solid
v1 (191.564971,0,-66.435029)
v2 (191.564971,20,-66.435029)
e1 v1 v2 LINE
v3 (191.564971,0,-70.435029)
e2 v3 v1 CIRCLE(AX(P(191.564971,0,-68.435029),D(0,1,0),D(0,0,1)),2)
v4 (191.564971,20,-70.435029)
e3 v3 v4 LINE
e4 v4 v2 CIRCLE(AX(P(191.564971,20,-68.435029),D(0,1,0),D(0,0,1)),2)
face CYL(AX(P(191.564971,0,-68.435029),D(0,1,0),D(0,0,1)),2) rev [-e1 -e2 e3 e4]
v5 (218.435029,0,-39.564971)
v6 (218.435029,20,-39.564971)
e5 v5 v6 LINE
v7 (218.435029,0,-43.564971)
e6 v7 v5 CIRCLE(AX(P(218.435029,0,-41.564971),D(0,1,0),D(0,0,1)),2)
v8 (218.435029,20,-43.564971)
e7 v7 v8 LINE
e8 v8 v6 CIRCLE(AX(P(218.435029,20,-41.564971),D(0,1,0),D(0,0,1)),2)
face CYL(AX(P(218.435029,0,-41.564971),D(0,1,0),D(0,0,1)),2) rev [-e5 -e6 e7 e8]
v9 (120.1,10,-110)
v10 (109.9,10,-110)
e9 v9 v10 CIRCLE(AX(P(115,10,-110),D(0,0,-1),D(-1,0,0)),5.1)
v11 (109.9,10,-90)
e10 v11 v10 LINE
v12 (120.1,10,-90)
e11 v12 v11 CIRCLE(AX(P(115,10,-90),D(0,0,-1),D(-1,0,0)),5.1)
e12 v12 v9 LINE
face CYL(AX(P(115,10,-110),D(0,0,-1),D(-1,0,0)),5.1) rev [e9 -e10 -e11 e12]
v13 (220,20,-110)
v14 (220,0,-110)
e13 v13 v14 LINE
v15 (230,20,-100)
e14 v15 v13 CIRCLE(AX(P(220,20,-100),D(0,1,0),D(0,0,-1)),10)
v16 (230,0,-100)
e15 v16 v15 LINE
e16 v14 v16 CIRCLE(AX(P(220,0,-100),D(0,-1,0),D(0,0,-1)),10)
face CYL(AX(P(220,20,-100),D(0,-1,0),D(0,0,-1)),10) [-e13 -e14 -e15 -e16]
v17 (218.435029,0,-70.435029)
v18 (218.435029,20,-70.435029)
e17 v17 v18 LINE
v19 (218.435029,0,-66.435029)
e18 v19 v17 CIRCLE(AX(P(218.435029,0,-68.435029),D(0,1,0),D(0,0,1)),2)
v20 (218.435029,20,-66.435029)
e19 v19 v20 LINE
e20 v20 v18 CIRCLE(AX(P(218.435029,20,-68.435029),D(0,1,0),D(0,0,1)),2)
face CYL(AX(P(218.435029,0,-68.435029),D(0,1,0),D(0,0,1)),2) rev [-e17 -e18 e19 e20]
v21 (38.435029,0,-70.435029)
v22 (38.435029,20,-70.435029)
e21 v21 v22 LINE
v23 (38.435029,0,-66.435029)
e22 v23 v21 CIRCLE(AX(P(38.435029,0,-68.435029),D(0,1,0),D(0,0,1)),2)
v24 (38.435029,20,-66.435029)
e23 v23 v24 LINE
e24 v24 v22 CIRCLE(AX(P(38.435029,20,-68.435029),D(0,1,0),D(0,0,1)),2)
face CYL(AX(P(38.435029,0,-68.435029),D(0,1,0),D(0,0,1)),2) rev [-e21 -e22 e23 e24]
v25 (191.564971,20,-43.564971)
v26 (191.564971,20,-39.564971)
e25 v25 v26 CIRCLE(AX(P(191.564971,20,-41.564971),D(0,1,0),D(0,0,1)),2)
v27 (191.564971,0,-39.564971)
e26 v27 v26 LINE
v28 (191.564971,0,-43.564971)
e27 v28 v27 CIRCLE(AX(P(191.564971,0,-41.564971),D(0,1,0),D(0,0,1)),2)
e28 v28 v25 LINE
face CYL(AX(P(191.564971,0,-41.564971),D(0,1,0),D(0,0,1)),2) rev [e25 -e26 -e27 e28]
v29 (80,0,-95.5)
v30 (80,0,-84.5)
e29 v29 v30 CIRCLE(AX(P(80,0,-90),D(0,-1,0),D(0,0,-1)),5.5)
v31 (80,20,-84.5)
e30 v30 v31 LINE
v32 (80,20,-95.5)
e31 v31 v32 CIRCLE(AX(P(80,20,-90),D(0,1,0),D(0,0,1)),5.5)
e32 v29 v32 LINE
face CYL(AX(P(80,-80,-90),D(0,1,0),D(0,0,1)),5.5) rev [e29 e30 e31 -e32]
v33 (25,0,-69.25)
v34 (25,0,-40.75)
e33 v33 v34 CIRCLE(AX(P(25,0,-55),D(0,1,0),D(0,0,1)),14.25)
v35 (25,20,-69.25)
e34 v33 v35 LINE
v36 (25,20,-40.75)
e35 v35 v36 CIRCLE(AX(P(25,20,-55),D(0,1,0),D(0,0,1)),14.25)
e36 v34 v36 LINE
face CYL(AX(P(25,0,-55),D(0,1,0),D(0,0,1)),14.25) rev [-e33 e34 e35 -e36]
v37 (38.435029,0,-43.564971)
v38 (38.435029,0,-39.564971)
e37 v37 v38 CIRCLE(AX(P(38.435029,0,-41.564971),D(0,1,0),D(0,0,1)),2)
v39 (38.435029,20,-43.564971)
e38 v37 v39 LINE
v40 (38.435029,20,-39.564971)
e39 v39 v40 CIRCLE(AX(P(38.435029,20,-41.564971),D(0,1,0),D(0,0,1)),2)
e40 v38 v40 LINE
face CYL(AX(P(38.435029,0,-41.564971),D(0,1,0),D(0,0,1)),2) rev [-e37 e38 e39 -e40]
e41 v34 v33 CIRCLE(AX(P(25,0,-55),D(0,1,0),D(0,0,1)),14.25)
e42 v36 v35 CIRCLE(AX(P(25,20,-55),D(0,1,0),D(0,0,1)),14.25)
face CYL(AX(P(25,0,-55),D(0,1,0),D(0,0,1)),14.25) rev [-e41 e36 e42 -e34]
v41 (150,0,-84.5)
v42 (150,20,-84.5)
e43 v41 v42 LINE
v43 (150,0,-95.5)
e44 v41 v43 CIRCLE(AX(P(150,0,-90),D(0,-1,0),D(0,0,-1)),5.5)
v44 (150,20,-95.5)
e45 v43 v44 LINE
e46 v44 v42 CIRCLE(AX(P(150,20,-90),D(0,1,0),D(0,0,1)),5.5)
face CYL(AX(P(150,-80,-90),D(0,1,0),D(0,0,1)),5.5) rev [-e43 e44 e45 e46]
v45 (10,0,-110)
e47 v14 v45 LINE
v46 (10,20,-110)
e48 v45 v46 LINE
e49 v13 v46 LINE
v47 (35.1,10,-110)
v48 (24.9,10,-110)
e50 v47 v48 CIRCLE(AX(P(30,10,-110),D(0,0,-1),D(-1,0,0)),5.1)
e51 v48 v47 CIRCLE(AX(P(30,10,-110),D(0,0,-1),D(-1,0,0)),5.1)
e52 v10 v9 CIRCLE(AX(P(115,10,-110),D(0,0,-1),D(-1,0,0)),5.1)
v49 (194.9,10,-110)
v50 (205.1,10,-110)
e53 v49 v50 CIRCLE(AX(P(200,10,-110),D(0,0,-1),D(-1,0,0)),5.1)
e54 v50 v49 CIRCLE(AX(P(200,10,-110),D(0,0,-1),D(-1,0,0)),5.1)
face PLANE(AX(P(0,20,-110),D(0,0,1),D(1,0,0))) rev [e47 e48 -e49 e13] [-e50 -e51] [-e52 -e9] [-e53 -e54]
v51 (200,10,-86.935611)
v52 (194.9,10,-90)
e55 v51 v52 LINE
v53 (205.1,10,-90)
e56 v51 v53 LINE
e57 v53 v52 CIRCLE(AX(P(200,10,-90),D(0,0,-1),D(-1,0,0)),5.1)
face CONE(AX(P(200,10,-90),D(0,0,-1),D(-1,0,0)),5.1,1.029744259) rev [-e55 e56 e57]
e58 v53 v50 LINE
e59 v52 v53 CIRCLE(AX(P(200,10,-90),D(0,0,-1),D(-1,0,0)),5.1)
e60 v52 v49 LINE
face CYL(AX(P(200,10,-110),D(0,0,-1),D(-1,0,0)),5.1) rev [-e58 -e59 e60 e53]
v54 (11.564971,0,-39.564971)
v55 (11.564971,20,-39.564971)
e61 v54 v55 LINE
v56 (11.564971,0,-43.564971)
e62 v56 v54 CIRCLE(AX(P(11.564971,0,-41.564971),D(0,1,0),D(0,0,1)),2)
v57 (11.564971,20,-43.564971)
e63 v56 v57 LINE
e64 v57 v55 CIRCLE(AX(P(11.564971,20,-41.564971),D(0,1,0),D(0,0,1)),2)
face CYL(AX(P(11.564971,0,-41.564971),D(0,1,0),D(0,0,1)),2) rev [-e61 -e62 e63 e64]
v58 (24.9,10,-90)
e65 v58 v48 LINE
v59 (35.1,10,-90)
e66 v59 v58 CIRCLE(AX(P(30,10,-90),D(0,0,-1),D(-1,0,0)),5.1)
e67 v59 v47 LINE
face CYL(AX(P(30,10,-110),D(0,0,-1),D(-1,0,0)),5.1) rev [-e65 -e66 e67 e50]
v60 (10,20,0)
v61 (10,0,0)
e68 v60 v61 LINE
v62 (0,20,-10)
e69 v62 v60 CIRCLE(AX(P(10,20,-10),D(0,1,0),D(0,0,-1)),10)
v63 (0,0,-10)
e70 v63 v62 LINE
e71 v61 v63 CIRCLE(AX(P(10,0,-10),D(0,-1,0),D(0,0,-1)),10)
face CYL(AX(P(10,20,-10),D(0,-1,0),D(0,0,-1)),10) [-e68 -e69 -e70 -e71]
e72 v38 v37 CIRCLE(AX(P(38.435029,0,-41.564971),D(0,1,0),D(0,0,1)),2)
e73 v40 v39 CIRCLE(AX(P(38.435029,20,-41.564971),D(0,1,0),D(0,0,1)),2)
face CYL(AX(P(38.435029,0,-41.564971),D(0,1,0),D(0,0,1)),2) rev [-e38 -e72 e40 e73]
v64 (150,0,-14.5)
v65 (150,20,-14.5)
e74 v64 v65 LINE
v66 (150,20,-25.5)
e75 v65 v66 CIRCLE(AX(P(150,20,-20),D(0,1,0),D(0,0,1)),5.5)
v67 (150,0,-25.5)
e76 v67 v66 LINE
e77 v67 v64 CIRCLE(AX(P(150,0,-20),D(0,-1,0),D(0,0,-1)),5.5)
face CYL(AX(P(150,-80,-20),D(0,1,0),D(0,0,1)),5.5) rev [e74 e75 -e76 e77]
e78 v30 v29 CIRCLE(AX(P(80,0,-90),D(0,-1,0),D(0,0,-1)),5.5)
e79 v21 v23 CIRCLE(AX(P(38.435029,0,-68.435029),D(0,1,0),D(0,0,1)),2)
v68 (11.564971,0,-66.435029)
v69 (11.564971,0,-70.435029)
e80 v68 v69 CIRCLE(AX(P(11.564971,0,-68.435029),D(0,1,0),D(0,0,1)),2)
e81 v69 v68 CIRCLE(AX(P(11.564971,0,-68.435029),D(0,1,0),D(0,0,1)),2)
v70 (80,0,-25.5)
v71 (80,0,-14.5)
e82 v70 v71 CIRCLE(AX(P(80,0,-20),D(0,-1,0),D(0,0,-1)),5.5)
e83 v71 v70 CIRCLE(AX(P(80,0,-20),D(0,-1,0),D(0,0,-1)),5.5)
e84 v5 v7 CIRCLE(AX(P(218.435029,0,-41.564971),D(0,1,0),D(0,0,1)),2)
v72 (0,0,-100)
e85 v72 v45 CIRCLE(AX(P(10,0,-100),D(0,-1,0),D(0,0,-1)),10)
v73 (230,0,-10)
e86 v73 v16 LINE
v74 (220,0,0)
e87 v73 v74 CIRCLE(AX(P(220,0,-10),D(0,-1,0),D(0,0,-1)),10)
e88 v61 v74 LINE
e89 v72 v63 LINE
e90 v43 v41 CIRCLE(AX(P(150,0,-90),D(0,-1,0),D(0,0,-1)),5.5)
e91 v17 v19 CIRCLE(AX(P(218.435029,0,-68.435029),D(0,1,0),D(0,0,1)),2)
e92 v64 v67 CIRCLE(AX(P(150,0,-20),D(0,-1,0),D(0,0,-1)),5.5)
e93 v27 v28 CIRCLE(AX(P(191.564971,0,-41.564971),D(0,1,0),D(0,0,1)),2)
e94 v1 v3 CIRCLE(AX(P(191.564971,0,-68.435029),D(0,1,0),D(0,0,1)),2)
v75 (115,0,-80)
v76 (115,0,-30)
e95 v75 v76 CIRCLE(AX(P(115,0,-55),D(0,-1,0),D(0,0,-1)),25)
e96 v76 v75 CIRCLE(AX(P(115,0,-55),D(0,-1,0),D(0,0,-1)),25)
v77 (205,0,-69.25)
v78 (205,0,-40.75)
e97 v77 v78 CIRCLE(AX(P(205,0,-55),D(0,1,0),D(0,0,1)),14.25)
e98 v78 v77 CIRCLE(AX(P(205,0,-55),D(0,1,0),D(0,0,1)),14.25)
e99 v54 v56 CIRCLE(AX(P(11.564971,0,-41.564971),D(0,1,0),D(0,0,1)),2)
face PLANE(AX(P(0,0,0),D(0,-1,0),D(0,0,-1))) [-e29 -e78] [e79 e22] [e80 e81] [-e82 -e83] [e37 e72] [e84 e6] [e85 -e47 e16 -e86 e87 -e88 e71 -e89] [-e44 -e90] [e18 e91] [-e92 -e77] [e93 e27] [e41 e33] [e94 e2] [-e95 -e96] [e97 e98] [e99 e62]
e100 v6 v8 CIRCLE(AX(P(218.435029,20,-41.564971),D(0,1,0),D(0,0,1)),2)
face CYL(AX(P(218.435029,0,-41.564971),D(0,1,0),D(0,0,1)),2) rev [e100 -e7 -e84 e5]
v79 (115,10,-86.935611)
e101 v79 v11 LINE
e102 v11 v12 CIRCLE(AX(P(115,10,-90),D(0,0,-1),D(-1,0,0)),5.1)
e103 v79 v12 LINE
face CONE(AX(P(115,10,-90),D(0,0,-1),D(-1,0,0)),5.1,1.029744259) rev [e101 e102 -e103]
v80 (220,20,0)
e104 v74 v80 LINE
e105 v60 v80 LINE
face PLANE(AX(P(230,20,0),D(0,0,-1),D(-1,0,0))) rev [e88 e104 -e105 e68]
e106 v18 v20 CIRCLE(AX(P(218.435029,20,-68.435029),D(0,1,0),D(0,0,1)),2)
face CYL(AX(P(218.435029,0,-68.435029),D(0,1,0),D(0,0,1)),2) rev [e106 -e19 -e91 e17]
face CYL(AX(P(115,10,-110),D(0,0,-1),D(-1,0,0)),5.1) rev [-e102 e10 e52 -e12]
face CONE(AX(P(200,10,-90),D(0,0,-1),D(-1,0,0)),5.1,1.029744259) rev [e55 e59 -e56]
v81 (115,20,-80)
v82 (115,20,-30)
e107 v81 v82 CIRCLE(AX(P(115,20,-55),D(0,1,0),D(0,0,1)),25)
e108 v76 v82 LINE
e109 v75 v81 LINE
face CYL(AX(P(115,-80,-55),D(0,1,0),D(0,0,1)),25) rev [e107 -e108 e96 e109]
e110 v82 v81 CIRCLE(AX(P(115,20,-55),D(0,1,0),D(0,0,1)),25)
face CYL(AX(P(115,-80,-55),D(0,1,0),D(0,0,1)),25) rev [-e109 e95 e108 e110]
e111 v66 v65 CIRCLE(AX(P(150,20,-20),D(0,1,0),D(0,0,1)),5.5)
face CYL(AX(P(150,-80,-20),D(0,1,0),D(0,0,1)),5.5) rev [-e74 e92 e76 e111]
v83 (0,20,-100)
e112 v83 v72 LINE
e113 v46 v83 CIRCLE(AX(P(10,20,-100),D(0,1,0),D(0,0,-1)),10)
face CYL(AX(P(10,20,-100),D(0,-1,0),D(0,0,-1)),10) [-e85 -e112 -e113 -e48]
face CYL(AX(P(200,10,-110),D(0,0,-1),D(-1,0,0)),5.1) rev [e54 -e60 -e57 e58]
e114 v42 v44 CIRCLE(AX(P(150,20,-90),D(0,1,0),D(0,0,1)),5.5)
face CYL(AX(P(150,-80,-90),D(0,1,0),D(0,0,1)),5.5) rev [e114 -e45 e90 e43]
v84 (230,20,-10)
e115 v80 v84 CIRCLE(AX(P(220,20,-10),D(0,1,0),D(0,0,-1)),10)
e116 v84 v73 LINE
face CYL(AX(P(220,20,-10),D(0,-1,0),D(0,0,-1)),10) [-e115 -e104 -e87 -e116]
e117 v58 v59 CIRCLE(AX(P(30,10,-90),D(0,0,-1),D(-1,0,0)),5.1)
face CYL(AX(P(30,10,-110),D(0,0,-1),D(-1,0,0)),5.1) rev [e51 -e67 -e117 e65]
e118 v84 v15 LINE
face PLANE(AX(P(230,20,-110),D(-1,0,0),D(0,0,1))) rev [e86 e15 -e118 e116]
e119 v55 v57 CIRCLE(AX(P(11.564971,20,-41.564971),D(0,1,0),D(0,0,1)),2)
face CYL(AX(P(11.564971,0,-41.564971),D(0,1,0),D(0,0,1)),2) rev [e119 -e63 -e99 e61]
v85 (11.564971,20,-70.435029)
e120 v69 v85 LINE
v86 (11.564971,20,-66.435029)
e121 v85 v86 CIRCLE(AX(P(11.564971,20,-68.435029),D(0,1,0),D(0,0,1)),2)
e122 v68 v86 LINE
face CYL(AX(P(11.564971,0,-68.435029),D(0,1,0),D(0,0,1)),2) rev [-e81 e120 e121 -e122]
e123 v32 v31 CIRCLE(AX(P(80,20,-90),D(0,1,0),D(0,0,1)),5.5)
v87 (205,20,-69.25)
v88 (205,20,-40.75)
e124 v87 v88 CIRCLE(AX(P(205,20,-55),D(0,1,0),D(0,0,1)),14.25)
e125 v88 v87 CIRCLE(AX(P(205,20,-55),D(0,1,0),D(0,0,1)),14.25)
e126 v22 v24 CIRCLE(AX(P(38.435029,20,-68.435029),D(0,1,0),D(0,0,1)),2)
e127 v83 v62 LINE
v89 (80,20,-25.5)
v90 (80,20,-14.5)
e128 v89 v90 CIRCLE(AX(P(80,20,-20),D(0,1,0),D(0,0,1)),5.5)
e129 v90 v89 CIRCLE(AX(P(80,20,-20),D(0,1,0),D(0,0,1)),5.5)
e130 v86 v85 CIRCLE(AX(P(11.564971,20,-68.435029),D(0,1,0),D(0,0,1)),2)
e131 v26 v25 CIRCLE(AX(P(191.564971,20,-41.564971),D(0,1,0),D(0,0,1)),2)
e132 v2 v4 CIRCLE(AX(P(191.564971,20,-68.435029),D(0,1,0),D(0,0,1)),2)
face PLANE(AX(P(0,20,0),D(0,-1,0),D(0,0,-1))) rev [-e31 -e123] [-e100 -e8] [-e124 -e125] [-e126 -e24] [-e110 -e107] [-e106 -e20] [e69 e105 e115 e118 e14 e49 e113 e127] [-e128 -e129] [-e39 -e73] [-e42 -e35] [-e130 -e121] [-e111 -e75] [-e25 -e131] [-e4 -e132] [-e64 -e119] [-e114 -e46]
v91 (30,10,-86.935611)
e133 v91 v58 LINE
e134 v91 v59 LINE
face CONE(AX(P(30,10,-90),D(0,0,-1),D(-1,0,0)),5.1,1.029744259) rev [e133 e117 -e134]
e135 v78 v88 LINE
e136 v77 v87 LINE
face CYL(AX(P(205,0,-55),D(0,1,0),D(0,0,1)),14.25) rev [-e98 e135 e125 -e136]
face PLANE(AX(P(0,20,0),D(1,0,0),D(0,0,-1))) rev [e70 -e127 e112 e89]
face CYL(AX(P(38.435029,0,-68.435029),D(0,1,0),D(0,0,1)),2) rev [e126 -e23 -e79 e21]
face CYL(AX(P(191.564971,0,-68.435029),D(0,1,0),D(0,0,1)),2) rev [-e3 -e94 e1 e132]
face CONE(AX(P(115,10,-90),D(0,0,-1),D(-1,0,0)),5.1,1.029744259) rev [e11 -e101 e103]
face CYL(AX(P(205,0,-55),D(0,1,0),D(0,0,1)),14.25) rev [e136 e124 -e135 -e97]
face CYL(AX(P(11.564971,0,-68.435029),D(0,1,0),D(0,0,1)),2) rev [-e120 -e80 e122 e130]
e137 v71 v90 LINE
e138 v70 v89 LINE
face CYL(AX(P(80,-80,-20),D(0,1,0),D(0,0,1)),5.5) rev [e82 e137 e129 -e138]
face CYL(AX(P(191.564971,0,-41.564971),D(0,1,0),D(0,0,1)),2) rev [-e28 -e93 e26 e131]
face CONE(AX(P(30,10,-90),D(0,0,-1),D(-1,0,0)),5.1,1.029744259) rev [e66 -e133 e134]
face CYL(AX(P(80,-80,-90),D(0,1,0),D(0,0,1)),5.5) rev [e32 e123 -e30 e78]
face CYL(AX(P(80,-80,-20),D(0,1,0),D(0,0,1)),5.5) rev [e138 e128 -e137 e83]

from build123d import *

# Parameters (mm, degrees)
SKETCH1_W              = 230
SKETCH1_H              = 110
BOSS_EXTRUDE1_DEPTH    = 20
SKETCH2_R              = 14.25
CUT_EXTRUDE2_DEPTH     = 256.734237051
SKETCH3_R              = 2
CUT_EXTRUDE3_DEPTH     = 256.734237051
LPATTERN1_COUNT        = 2
LPATTERN1_PITCH        = 180
FILLET1_R              = 10
SKETCH4_R              = 25
SKETCH4_R_2            = 5.5
CUT_EXTRUDE4_DEPTH     = 100
M12_TAPPED_HOLE2_D     = 10.2
M12_TAPPED_HOLE2_DEPTH = 20
M12_TAPPED_HOLE2_TIP   = 3.064389157


with BuildPart() as part:
    # Sketch1 → Boss-Extrude1 (new body)
    with BuildSketch(Plane(origin=(0, 0, 0), x_dir=(1, 0, 0), z_dir=(0, 1, 0))):
        with Locations((115, 55)):
            Rectangle(SKETCH1_W, SKETCH1_H)
    extrude(amount=BOSS_EXTRUDE1_DEPTH)

    # Sketch2 → Cut-Extrude2 (cut, through all)
    with BuildSketch(Plane(origin=(0, 20, 0), x_dir=(1, 0, 0), z_dir=(0, 1, 0))):
        with Locations(Location((25, 55, 0), (0, 0, 270))):
            Circle(SKETCH2_R)
        with Locations(Location((205, 55, 0), (0, 0, 270))):
            Circle(SKETCH2_R)
    extrude(amount=-CUT_EXTRUDE2_DEPTH, mode=Mode.SUBTRACT)

    # Sketch3 → Cut-Extrude3 (cut, through all)
    with BuildSketch(Plane(origin=(0, 20, 0), x_dir=(1, 0, 0), z_dir=(0, 1, 0))):
        with Locations(Location((11.564971157, 68.435028843, 0), (0, 0, 270))):
            Circle(SKETCH3_R)
        with Locations(Location((38.435028843, 68.435028843, 0), (0, 0, 270))):
            Circle(SKETCH3_R)
        with Locations(Location((38.435028843, 41.564971157, 0), (0, 0, 270))):
            Circle(SKETCH3_R)
        with Locations(Location((11.564971157, 41.564971157, 0), (0, 0, 270))):
            Circle(SKETCH3_R)
    cut_extrude3 = extrude(amount=-CUT_EXTRUDE3_DEPTH, mode=Mode.SUBTRACT)

    # LPattern1: Cut-Extrude3 ×2
    with Locations(*[(i * LPATTERN1_PITCH, 0, 0) for i in range(1, LPATTERN1_COUNT)]):
        add(cut_extrude3, mode=Mode.SUBTRACT)

    # Fillet1
    fillet1_edges = [part.edges().sort_by_distance(p)[0] for p in [
        (0, 10, 0),
        (0, 10, -110),
        (230, 10, -110),
        (230, 10, 0),
    ]]
    fillet(fillet1_edges, radius=FILLET1_R)

    # Sketch4 → Cut-Extrude4 (cut)
    with BuildSketch(Plane(origin=(0, 20, 0), x_dir=(1, 0, 0), z_dir=(0, 1, 0))):
        with Locations(Location((115, 55, 0), (0, 0, 270))):
            Circle(SKETCH4_R)
        with Locations(Location((150, 90, 0), (0, 0, 270))):
            Circle(SKETCH4_R_2)
        with Locations(Location((150, 20, 0), (0, 0, 270))):
            Circle(SKETCH4_R_2)
        with Locations(Location((80, 20, 0), (0, 0, 270))):
            Circle(SKETCH4_R_2)
        with Locations(Location((80, 90, 0), (0, 0, 270))):
            Circle(SKETCH4_R_2)
    extrude(amount=-CUT_EXTRUDE4_DEPTH, mode=Mode.SUBTRACT)

    # M12 Tapped Hole2
    with Locations(Plane(origin=(0, 0, -110), x_dir=(-1, 0, 0), z_dir=(0, 0, -1))):
        with Locations((-200, 10), (-115, 10), (-30, 10)):
            Hole(M12_TAPPED_HOLE2_D / 2, depth=M12_TAPPED_HOLE2_DEPTH)
            with Locations((0, 0, -(M12_TAPPED_HOLE2_DEPTH + M12_TAPPED_HOLE2_TIP / 2))):  # 118° drill point
                Cone(0, M12_TAPPED_HOLE2_D / 2, M12_TAPPED_HOLE2_TIP, mode=Mode.SUBTRACT)


solid = part.part
